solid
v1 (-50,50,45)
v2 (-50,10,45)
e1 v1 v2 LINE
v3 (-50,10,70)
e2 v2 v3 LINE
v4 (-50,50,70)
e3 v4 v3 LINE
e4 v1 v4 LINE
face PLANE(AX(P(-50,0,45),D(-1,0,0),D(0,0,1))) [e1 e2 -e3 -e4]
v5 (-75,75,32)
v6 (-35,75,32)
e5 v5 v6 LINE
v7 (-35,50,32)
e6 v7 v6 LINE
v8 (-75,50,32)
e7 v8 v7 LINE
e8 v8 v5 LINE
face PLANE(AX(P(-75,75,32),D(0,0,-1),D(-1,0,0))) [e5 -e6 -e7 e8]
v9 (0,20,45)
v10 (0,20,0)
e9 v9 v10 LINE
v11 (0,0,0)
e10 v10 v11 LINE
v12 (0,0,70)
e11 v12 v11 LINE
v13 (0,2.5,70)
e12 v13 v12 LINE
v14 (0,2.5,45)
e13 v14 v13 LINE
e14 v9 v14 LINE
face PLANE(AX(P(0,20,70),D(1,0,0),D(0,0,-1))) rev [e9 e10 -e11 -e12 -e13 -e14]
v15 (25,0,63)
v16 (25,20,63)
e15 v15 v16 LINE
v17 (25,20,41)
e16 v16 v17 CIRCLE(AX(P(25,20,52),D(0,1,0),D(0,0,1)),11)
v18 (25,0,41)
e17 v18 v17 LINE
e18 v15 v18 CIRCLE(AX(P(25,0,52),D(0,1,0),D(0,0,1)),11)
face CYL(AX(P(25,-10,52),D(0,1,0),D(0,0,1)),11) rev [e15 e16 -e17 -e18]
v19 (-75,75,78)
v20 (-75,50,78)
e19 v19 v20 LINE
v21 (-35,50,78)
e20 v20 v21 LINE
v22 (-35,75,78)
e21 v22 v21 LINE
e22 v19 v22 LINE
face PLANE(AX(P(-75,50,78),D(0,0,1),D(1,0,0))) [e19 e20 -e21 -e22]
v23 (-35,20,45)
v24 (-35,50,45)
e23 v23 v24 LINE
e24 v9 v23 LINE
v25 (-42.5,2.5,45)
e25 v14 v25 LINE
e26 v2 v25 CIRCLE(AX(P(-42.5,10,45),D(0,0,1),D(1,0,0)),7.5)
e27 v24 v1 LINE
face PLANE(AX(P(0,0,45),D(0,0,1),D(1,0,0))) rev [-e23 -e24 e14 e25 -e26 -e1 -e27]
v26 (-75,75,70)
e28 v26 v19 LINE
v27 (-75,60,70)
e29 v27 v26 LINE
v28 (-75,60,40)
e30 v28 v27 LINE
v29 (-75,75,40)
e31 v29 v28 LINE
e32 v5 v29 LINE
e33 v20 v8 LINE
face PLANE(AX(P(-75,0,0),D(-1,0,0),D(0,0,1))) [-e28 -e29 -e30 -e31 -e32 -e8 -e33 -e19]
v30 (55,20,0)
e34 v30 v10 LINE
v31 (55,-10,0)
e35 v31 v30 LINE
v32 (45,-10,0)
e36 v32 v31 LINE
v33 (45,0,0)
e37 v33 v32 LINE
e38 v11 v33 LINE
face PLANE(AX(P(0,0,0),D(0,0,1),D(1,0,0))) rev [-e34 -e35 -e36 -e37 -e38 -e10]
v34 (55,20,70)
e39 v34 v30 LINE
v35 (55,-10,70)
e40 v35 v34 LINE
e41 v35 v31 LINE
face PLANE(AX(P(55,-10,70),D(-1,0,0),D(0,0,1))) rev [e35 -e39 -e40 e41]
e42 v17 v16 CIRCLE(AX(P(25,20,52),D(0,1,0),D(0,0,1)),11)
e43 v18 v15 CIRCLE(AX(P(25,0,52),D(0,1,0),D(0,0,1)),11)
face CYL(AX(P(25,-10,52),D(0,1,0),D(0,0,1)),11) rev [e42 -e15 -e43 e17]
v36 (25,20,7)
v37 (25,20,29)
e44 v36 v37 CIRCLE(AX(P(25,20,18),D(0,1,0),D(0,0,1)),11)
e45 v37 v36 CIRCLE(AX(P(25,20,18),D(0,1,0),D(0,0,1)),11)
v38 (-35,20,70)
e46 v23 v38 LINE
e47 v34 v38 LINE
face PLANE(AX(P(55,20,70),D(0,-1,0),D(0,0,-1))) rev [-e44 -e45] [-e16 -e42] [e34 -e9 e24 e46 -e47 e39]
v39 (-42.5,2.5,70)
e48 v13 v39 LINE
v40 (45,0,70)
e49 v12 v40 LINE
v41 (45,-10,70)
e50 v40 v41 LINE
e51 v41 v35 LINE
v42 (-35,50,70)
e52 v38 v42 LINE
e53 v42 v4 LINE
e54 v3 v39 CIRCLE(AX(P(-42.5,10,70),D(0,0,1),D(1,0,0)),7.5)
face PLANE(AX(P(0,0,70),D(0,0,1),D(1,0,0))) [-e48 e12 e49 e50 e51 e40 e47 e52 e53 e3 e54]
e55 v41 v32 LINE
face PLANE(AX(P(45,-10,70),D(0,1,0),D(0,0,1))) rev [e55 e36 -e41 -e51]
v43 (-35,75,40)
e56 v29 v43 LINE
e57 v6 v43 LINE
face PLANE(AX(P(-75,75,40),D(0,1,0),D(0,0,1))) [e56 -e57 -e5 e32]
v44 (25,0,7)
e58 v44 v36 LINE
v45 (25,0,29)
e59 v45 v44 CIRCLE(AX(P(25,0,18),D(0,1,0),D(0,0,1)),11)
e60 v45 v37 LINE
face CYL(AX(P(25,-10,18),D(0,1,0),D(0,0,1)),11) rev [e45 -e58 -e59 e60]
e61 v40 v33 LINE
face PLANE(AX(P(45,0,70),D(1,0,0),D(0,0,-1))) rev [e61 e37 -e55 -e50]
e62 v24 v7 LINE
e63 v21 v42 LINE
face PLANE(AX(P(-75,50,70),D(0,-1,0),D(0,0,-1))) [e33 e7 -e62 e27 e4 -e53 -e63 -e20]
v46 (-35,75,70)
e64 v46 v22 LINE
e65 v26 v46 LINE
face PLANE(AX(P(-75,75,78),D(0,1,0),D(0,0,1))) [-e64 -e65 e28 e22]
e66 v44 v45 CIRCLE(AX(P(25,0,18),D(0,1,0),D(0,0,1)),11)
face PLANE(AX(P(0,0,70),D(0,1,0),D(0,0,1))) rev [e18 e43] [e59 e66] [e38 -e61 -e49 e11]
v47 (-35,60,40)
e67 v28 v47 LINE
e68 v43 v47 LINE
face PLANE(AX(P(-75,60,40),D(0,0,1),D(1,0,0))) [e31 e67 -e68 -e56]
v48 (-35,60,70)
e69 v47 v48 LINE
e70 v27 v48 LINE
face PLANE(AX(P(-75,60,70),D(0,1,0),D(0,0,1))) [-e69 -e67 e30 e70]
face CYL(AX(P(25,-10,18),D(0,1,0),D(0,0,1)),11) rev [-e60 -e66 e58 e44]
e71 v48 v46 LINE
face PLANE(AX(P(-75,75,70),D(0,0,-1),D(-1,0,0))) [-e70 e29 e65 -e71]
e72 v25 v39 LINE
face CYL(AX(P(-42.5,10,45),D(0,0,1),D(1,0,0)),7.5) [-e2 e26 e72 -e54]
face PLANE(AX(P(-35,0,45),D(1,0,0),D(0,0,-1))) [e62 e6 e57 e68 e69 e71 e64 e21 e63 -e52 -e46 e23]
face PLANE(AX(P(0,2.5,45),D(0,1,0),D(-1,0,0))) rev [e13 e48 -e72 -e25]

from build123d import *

# Parameters (mm, degrees)
BASE_BRACKET_DEPTH     = 70
UPRIGHT_POST_DEPTH     = 25
SLOTTED_HEAD_DEPTH     = 40
BASE_HOLES_SKETCH_R    = 11
BASE_HOLES_2X_22_DEPTH = 30


with BuildPart() as part:
    # Base Bracket Profile Sketch → Base Bracket (new body)
    with BuildSketch(Plane.XY):
        Polygon((0, 0), (45, 0), (45, -10), (55, -10), (55, 20), (0, 20), align=None)
    extrude(amount=BASE_BRACKET_DEPTH)

    # Upright Post Sketch → Upright Post (add)
    with BuildSketch(Plane.XY.offset(70)):
        with BuildLine():
            Line((-50, 50), (-50, 10))
            ThreePointArc((-50, 10), (-47.803300859, 4.696699141), (-42.5, 2.5))
            Line((-42.5, 2.5), (0, 2.5))
            Line((0, 2.5), (0, 20))
            Line((0, 20), (-35, 20))
            Line((-35, 20), (-35, 50))
            Line((-35, 50), (-50, 50))
        make_face()
    extrude(amount=-UPRIGHT_POST_DEPTH)

    # Slotted Head Profile Sketch → Slotted Head (add)
    with BuildSketch(Plane(origin=(-35, 0, 0), x_dir=(0, 0, -1), z_dir=(1, 0, 0))):
        Polygon((-70, 50), (-78, 50), (-78, 75), (-70, 75), (-70, 60), (-40, 60), (-40, 75), (-32, 75), (-32, 50), align=None)
    extrude(amount=-SLOTTED_HEAD_DEPTH)

    # Base Holes Sketch → Base Holes 2xØ22 (cut)
    with BuildSketch(Plane(origin=(0, 20, 0), x_dir=(1, 0, 0), z_dir=(0, 1, 0))):
        with Locations(Location((25, -18, 0), (0, 0, 270))):
            Circle(BASE_HOLES_SKETCH_R)
        with Locations(Location((25, -52, 0), (0, 0, 270))):
            Circle(BASE_HOLES_SKETCH_R)
    extrude(amount=-BASE_HOLES_2X_22_DEPTH, mode=Mode.SUBTRACT)


solid = part.part
